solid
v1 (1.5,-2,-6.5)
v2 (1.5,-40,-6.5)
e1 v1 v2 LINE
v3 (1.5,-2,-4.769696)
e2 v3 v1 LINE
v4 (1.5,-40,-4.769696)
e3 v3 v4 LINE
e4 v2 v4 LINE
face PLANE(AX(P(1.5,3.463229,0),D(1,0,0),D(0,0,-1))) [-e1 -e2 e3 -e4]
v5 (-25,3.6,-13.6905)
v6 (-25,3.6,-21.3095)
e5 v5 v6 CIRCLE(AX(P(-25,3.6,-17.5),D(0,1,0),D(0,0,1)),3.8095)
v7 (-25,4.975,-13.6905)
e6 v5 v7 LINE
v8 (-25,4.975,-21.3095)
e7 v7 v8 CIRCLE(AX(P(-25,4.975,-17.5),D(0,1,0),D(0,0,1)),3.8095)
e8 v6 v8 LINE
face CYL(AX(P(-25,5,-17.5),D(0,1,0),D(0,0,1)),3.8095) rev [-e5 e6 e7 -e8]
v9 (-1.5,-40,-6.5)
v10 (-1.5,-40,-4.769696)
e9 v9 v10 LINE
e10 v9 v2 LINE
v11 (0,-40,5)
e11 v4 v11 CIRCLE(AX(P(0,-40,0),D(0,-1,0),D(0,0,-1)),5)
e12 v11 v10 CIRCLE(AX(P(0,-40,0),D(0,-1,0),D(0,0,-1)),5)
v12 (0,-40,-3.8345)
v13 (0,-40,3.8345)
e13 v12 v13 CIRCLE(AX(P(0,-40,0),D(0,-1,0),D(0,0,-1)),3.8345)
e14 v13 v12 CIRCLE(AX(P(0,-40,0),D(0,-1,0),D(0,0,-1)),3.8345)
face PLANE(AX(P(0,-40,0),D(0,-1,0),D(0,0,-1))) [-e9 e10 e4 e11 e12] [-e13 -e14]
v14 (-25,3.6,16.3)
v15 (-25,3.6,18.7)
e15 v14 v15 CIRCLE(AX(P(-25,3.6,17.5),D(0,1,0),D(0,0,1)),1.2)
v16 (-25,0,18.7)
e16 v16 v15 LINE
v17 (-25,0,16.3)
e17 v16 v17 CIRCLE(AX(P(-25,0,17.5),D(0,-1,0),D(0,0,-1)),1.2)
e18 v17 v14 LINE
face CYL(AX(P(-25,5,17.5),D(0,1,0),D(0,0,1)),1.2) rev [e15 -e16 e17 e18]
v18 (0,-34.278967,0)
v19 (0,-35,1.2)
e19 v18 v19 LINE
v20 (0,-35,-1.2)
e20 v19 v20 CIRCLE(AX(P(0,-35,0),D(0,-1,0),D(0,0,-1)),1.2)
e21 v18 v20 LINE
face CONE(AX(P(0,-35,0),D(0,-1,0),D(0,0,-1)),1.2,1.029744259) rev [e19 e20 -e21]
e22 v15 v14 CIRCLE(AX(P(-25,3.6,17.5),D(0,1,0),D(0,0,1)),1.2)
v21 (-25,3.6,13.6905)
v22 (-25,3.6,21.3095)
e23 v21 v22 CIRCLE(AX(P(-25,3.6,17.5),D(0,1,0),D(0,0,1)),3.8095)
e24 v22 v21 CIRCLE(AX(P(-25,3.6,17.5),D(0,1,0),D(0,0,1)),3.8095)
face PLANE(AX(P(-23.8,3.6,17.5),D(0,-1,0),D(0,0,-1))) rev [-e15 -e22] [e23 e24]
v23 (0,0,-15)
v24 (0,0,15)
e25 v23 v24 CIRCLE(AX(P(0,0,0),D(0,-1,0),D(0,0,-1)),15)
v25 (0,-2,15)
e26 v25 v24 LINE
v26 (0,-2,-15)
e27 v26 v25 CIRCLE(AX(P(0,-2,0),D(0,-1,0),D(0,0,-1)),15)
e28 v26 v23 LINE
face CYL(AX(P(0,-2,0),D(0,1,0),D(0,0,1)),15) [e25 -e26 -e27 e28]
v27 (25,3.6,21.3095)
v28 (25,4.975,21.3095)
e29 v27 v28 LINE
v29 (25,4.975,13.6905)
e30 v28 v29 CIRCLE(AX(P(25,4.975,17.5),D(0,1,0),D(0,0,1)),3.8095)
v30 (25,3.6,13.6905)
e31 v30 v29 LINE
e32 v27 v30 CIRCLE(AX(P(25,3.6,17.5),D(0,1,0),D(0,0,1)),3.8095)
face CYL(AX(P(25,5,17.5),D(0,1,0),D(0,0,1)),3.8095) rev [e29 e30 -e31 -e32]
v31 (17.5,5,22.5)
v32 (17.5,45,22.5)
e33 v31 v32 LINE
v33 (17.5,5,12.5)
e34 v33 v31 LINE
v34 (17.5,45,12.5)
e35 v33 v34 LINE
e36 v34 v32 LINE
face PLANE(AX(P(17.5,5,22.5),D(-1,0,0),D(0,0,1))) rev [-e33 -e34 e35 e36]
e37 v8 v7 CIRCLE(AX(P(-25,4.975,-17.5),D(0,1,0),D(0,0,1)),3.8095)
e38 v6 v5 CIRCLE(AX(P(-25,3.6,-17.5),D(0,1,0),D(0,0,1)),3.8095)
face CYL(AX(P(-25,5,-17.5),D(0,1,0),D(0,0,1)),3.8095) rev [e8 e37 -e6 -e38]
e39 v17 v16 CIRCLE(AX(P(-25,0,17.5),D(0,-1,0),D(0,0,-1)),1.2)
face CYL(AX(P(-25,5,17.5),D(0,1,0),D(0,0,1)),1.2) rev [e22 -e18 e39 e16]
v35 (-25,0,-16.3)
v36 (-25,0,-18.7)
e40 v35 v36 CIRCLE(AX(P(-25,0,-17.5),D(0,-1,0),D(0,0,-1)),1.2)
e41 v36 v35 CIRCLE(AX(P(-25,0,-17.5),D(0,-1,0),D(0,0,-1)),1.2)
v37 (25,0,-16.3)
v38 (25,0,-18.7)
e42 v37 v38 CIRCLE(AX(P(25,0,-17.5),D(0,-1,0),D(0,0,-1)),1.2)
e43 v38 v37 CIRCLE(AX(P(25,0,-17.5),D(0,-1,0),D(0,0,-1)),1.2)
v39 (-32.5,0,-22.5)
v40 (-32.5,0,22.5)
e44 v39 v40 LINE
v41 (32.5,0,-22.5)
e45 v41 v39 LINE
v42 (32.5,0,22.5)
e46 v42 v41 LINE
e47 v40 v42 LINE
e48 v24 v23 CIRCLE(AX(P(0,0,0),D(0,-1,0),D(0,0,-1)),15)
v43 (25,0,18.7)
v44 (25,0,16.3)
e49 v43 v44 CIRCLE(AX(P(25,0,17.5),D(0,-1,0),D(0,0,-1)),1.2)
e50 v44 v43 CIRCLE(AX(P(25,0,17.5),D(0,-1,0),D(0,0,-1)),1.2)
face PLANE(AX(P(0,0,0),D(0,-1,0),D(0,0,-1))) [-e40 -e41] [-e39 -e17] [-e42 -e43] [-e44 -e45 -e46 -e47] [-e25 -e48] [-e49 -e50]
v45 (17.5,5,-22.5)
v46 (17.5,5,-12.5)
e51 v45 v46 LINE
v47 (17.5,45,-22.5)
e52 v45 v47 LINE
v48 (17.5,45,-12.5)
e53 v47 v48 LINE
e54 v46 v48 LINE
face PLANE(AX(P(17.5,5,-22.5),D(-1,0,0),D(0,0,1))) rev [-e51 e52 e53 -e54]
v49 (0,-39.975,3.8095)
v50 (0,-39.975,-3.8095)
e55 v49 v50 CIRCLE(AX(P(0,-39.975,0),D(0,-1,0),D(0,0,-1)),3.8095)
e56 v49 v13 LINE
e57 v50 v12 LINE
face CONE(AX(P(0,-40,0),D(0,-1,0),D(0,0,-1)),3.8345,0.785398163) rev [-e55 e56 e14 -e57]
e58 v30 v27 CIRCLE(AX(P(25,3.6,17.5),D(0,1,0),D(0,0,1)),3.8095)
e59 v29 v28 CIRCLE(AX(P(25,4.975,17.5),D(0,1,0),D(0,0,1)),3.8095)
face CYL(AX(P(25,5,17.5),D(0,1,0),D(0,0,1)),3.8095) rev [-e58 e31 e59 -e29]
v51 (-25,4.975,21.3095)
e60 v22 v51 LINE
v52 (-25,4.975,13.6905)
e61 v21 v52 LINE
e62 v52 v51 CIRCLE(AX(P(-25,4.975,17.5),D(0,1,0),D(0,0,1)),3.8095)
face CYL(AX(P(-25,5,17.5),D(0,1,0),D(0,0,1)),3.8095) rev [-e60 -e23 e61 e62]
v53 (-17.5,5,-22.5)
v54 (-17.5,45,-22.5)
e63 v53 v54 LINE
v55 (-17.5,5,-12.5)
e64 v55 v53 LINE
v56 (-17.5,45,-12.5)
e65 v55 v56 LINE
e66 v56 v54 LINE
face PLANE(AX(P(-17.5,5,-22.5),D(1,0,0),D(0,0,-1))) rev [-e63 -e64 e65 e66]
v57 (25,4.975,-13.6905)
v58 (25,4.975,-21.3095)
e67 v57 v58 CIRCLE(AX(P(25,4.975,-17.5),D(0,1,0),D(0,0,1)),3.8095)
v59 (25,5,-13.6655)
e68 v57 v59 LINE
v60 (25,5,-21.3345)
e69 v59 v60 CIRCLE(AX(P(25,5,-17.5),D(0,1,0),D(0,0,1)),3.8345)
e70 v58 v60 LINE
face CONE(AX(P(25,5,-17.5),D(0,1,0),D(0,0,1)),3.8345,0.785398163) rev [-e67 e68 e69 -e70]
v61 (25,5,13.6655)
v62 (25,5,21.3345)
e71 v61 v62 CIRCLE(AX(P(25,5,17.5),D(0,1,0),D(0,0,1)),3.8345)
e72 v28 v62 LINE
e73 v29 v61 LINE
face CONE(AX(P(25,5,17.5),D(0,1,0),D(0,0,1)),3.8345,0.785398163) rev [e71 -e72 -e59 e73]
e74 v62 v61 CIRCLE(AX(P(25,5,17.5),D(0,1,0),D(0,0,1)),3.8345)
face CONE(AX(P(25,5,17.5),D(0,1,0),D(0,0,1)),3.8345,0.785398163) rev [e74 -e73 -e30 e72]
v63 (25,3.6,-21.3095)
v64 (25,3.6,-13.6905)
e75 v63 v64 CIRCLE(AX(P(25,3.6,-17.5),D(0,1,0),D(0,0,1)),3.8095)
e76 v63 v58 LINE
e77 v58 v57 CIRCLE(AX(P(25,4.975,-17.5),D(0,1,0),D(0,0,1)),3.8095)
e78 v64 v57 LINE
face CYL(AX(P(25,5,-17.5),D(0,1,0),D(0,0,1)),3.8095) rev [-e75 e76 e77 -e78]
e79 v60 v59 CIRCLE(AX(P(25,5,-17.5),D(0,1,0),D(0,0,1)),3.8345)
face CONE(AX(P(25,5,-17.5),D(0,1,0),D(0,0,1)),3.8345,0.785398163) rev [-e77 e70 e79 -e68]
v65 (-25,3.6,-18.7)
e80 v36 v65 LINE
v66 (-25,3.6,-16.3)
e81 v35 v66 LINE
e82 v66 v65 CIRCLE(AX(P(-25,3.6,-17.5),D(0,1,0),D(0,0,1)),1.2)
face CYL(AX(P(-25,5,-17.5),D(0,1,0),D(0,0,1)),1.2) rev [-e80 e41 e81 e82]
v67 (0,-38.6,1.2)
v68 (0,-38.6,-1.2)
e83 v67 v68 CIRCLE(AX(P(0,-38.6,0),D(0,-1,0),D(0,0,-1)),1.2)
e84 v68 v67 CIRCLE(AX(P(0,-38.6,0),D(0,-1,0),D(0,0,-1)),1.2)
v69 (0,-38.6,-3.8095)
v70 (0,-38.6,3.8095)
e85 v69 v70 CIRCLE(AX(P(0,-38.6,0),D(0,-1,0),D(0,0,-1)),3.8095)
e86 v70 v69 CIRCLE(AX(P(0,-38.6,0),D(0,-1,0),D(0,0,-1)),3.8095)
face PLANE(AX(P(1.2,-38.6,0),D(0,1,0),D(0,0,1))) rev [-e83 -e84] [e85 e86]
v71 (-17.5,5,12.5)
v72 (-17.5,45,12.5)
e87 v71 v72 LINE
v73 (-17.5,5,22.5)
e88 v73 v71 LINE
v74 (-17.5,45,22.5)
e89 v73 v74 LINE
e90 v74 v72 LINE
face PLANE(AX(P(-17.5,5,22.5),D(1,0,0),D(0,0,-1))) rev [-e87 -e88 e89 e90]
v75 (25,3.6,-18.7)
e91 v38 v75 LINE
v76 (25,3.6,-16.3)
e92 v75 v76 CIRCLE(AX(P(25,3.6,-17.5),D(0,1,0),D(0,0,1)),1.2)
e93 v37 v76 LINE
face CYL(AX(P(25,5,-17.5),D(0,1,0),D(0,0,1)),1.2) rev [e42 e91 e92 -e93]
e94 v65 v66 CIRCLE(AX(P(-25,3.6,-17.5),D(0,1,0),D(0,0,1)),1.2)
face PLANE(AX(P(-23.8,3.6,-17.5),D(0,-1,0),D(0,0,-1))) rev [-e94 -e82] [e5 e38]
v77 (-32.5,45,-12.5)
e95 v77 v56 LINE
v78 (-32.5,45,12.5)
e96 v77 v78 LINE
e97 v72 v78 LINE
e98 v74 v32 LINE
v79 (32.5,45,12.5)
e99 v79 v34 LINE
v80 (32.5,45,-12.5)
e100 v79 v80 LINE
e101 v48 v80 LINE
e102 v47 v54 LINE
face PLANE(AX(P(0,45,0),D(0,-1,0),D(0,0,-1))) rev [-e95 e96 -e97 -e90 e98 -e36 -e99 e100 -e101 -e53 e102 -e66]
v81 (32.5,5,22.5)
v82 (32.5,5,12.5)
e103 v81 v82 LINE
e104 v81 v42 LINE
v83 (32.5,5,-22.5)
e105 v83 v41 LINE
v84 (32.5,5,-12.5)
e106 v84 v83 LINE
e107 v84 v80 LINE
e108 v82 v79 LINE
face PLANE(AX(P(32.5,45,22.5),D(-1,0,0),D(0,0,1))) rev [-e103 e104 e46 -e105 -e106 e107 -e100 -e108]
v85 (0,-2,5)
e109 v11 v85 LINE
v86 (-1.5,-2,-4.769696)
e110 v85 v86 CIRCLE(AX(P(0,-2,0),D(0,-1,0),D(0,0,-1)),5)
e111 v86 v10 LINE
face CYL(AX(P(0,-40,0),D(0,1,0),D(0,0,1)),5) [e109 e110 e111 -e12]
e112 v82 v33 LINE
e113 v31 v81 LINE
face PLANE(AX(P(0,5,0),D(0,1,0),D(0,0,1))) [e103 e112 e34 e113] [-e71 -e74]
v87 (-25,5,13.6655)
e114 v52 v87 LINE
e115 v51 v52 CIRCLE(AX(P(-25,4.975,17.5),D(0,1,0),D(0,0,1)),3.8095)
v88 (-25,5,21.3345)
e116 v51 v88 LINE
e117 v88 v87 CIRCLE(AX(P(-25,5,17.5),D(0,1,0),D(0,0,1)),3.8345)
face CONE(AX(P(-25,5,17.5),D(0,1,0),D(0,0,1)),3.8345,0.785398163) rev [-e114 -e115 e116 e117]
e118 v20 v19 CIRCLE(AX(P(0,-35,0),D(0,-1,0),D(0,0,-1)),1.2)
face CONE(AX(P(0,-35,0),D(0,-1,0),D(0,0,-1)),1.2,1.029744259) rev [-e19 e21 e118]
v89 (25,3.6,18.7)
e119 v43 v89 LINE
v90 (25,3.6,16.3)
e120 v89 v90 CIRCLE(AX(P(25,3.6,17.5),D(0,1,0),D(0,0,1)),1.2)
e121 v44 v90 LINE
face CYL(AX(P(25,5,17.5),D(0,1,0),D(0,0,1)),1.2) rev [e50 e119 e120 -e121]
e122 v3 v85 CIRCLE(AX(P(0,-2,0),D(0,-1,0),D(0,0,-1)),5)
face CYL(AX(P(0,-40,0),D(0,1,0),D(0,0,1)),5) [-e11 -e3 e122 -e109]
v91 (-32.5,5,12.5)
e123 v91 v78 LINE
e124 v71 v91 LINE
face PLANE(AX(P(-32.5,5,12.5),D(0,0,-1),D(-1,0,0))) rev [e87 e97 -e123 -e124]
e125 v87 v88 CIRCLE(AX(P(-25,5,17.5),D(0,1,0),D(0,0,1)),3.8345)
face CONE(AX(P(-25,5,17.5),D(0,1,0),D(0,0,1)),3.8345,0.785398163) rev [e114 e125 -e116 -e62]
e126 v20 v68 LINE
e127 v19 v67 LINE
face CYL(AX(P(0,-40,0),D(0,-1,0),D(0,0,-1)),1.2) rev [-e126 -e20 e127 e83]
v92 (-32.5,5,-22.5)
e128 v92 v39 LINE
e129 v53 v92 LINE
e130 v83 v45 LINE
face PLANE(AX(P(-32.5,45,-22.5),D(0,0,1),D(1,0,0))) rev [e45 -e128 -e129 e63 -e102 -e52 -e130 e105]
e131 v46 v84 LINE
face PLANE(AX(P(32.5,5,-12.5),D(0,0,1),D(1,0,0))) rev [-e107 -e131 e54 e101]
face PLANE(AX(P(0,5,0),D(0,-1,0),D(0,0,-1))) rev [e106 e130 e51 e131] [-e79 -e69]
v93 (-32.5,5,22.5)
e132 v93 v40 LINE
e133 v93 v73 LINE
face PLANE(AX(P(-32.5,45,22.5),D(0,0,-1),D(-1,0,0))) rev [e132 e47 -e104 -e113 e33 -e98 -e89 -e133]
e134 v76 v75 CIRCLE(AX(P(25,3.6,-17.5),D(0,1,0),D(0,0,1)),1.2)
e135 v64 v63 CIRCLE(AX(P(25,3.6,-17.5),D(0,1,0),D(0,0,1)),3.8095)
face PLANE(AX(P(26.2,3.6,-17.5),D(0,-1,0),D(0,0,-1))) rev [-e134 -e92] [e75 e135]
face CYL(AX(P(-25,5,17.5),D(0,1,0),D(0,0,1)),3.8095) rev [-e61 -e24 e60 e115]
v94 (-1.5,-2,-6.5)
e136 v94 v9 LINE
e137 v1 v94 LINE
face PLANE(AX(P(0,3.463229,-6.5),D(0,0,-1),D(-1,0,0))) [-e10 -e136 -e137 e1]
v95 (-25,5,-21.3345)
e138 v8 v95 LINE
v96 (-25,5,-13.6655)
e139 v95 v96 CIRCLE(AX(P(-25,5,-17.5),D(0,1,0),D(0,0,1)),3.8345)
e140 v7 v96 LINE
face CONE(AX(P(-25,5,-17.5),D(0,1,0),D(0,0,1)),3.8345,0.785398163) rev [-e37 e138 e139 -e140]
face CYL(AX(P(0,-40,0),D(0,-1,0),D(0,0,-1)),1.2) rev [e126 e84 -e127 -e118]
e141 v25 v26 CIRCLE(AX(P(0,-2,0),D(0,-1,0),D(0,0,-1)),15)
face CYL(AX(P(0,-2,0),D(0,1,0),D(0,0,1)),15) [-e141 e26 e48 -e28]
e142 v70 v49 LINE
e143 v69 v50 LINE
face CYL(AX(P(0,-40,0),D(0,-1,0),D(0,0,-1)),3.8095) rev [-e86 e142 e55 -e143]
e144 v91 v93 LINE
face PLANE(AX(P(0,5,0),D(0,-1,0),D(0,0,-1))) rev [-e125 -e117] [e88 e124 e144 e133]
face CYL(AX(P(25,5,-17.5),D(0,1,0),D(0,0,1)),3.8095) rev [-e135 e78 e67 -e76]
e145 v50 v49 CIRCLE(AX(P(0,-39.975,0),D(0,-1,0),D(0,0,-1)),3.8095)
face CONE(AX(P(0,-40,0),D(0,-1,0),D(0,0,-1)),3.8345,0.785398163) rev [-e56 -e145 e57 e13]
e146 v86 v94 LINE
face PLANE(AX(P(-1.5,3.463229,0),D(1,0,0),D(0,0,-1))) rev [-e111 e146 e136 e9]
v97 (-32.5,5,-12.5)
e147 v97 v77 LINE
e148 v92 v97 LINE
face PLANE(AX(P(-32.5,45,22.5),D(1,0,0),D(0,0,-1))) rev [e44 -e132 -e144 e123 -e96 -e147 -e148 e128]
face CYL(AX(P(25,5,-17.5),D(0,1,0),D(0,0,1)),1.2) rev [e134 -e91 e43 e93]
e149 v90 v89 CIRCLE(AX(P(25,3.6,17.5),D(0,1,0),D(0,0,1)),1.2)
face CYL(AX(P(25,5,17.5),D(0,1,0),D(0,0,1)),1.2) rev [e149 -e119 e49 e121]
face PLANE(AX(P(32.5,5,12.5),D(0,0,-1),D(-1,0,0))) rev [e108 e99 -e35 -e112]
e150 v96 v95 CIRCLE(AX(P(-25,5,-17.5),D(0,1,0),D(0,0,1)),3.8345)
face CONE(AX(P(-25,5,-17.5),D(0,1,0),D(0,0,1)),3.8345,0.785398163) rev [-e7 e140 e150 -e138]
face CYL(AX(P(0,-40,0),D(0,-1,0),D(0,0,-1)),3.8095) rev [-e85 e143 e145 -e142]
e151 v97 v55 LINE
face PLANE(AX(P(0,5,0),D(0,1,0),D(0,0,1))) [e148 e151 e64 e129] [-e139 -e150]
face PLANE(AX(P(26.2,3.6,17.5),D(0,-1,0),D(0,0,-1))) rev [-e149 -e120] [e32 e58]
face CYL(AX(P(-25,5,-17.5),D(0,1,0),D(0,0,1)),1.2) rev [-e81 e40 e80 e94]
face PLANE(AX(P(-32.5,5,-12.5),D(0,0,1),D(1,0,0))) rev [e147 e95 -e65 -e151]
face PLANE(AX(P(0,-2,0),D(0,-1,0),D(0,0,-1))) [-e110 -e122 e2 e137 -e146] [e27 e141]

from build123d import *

# Parameters (mm, degrees)
SKETCH1_W                              = 65
SKETCH1_H                              = 45
BOSS_EXTRUDE1_DEPTH                    = 45
SKETCH2_W                              = 15
SKETCH2_H                              = 10
CUT_EXTRUDE1_DEPTH                     = 40
SKETCH3_R                              = 5
BOSS_EXTRUDE2_DEPTH                    = 40
BOSS_EXTRUDE3_START                    = -40
BOSS_EXTRUDE3_DEPTH                    = 40
SKETCH5_R                              = 15
BOSS_EXTRUDE4_DEPTH                    = 2
CBORE_FOR_M2_HEX_CAP_SCREW2_AT_2_COUNT = 2
CBORE_FOR_M2_HEX_CAP_SCREW2_AT_2_PITCH = 50
CBORE_FOR_M2_HEX_CAP_SCREW2_AT_3_COUNT = 2
CBORE_FOR_M2_HEX_CAP_SCREW2_AT_3_PITCH = 35
CBORE_FOR_M2_HEX_CAP_SCREW2_AT_4_COUNT = 2
CBORE_FOR_M2_HEX_CAP_SCREW2_AT_4_PITCH = 61.032778079


with BuildPart() as part:
    # Sketch1 → Boss-Extrude1 (new body)
    with BuildSketch(Plane(origin=(0, 0, 0), x_dir=(1, 0, 0), z_dir=(0, 1, 0))):
        Rectangle(SKETCH1_W, SKETCH1_H)
    extrude(amount=BOSS_EXTRUDE1_DEPTH)

    # Sketch2 → Cut-Extrude1 (cut)
    with BuildSketch(Plane(origin=(0, 45, 0), x_dir=(1, 0, 0), z_dir=(0, 1, 0))):
        with Locations((-25, 17.5)):
            Rectangle(SKETCH2_W, SKETCH2_H)
        with Locations((-25, -17.5)):
            Rectangle(SKETCH2_W, SKETCH2_H)
        with Locations((25, -17.5)):
            Rectangle(SKETCH2_W, SKETCH2_H)
        with Locations((25, 17.5)):
            Rectangle(SKETCH2_W, SKETCH2_H)
    extrude(amount=-CUT_EXTRUDE1_DEPTH, mode=Mode.SUBTRACT)

    # Sketch3 → Boss-Extrude2 (add)
    with BuildSketch(Plane.XZ):
        with Locations(Location((0, 0, 0), (0, 0, 270))):
            Circle(SKETCH3_R)
    extrude(amount=BOSS_EXTRUDE2_DEPTH)

    # Sketch4 → Boss-Extrude3 (add)
    with BuildSketch(Plane.XZ.offset(40).offset(BOSS_EXTRUDE3_START)):
        with BuildLine():
            ThreePointArc((1.5, -4.769696007), (0.758788496, -4.942088629), (0, -5))
            ThreePointArc((0, -5), (-0.758788496, -4.942088629), (-1.5, -4.769696007))
            Line((-1.5, -4.769696007), (-1.5, -6.5))
            Line((-1.5, -6.5), (1.5, -6.5))
            Line((1.5, -6.5), (1.5, -4.769696007))
        make_face()
    extrude(amount=BOSS_EXTRUDE3_DEPTH)

    # Sketch5 → Boss-Extrude4 (add)
    with BuildSketch(Plane.XZ):
        with Locations(Location((0, 0, 0), (0, 0, 270))):
            Circle(SKETCH5_R)
    extrude(amount=BOSS_EXTRUDE4_DEPTH)

    # Sketch8 → CBORE for M2 Hex Cap Screw1 (revolve, cut)
    with BuildSketch(Plane(origin=(0, -40, 0), x_dir=(0, 0, -1), z_dir=(1, 0, 0))):
        Polygon((0, 0), (0, 5.721032743), (1.2, 5), (1.2, 1.4), (3.8095, 1.4), (3.8095, 0.025), (3.8345, 0), align=None)
    revolve(axis=Axis((0, -46.35, 0), (0, 1, 0)), mode=Mode.SUBTRACT)

    # Sketch12 → CBORE for M2 Hex Cap Screw2 (revolve, cut)
    with BuildSketch(Plane(origin=(-25, 5, -17.5), x_dir=(0, 0, 1), z_dir=(1, 0, 0))):
        Polygon((0, 0), (0, 10.721032743), (1.2, 10), (1.2, 1.4), (3.8095, 1.4), (3.8095, 0.025), (3.8345, 0), align=None)
    cbore_for_m2_hex_cap_screw2 = revolve(axis=Axis((-25, 11.35, -17.5), (0, -1, 0)), mode=Mode.SUBTRACT)

    # CBORE for M2 Hex Cap Screw2 at 2: CBORE for M2 Hex Cap Screw2 ×2
    with Locations(*[(i * CBORE_FOR_M2_HEX_CAP_SCREW2_AT_2_PITCH, 0, 0) for i in range(1, CBORE_FOR_M2_HEX_CAP_SCREW2_AT_2_COUNT)]):
        add(cbore_for_m2_hex_cap_screw2, mode=Mode.SUBTRACT)

    # CBORE for M2 Hex Cap Screw2 at 3: CBORE for M2 Hex Cap Screw2 ×2
    with Locations(*[(0, 0, i * CBORE_FOR_M2_HEX_CAP_SCREW2_AT_3_PITCH) for i in range(1, CBORE_FOR_M2_HEX_CAP_SCREW2_AT_3_COUNT)]):
        add(cbore_for_m2_hex_cap_screw2, mode=Mode.SUBTRACT)

    # CBORE for M2 Hex Cap Screw2 at 4: CBORE for M2 Hex Cap Screw2 ×2
    with Locations(*[Vector(0.8192319205190405, 0, 0.5734623443633283) * (i * CBORE_FOR_M2_HEX_CAP_SCREW2_AT_4_PITCH) for i in range(1, CBORE_FOR_M2_HEX_CAP_SCREW2_AT_4_COUNT)]):
        add(cbore_for_m2_hex_cap_screw2, mode=Mode.SUBTRACT)


solid = part.part
